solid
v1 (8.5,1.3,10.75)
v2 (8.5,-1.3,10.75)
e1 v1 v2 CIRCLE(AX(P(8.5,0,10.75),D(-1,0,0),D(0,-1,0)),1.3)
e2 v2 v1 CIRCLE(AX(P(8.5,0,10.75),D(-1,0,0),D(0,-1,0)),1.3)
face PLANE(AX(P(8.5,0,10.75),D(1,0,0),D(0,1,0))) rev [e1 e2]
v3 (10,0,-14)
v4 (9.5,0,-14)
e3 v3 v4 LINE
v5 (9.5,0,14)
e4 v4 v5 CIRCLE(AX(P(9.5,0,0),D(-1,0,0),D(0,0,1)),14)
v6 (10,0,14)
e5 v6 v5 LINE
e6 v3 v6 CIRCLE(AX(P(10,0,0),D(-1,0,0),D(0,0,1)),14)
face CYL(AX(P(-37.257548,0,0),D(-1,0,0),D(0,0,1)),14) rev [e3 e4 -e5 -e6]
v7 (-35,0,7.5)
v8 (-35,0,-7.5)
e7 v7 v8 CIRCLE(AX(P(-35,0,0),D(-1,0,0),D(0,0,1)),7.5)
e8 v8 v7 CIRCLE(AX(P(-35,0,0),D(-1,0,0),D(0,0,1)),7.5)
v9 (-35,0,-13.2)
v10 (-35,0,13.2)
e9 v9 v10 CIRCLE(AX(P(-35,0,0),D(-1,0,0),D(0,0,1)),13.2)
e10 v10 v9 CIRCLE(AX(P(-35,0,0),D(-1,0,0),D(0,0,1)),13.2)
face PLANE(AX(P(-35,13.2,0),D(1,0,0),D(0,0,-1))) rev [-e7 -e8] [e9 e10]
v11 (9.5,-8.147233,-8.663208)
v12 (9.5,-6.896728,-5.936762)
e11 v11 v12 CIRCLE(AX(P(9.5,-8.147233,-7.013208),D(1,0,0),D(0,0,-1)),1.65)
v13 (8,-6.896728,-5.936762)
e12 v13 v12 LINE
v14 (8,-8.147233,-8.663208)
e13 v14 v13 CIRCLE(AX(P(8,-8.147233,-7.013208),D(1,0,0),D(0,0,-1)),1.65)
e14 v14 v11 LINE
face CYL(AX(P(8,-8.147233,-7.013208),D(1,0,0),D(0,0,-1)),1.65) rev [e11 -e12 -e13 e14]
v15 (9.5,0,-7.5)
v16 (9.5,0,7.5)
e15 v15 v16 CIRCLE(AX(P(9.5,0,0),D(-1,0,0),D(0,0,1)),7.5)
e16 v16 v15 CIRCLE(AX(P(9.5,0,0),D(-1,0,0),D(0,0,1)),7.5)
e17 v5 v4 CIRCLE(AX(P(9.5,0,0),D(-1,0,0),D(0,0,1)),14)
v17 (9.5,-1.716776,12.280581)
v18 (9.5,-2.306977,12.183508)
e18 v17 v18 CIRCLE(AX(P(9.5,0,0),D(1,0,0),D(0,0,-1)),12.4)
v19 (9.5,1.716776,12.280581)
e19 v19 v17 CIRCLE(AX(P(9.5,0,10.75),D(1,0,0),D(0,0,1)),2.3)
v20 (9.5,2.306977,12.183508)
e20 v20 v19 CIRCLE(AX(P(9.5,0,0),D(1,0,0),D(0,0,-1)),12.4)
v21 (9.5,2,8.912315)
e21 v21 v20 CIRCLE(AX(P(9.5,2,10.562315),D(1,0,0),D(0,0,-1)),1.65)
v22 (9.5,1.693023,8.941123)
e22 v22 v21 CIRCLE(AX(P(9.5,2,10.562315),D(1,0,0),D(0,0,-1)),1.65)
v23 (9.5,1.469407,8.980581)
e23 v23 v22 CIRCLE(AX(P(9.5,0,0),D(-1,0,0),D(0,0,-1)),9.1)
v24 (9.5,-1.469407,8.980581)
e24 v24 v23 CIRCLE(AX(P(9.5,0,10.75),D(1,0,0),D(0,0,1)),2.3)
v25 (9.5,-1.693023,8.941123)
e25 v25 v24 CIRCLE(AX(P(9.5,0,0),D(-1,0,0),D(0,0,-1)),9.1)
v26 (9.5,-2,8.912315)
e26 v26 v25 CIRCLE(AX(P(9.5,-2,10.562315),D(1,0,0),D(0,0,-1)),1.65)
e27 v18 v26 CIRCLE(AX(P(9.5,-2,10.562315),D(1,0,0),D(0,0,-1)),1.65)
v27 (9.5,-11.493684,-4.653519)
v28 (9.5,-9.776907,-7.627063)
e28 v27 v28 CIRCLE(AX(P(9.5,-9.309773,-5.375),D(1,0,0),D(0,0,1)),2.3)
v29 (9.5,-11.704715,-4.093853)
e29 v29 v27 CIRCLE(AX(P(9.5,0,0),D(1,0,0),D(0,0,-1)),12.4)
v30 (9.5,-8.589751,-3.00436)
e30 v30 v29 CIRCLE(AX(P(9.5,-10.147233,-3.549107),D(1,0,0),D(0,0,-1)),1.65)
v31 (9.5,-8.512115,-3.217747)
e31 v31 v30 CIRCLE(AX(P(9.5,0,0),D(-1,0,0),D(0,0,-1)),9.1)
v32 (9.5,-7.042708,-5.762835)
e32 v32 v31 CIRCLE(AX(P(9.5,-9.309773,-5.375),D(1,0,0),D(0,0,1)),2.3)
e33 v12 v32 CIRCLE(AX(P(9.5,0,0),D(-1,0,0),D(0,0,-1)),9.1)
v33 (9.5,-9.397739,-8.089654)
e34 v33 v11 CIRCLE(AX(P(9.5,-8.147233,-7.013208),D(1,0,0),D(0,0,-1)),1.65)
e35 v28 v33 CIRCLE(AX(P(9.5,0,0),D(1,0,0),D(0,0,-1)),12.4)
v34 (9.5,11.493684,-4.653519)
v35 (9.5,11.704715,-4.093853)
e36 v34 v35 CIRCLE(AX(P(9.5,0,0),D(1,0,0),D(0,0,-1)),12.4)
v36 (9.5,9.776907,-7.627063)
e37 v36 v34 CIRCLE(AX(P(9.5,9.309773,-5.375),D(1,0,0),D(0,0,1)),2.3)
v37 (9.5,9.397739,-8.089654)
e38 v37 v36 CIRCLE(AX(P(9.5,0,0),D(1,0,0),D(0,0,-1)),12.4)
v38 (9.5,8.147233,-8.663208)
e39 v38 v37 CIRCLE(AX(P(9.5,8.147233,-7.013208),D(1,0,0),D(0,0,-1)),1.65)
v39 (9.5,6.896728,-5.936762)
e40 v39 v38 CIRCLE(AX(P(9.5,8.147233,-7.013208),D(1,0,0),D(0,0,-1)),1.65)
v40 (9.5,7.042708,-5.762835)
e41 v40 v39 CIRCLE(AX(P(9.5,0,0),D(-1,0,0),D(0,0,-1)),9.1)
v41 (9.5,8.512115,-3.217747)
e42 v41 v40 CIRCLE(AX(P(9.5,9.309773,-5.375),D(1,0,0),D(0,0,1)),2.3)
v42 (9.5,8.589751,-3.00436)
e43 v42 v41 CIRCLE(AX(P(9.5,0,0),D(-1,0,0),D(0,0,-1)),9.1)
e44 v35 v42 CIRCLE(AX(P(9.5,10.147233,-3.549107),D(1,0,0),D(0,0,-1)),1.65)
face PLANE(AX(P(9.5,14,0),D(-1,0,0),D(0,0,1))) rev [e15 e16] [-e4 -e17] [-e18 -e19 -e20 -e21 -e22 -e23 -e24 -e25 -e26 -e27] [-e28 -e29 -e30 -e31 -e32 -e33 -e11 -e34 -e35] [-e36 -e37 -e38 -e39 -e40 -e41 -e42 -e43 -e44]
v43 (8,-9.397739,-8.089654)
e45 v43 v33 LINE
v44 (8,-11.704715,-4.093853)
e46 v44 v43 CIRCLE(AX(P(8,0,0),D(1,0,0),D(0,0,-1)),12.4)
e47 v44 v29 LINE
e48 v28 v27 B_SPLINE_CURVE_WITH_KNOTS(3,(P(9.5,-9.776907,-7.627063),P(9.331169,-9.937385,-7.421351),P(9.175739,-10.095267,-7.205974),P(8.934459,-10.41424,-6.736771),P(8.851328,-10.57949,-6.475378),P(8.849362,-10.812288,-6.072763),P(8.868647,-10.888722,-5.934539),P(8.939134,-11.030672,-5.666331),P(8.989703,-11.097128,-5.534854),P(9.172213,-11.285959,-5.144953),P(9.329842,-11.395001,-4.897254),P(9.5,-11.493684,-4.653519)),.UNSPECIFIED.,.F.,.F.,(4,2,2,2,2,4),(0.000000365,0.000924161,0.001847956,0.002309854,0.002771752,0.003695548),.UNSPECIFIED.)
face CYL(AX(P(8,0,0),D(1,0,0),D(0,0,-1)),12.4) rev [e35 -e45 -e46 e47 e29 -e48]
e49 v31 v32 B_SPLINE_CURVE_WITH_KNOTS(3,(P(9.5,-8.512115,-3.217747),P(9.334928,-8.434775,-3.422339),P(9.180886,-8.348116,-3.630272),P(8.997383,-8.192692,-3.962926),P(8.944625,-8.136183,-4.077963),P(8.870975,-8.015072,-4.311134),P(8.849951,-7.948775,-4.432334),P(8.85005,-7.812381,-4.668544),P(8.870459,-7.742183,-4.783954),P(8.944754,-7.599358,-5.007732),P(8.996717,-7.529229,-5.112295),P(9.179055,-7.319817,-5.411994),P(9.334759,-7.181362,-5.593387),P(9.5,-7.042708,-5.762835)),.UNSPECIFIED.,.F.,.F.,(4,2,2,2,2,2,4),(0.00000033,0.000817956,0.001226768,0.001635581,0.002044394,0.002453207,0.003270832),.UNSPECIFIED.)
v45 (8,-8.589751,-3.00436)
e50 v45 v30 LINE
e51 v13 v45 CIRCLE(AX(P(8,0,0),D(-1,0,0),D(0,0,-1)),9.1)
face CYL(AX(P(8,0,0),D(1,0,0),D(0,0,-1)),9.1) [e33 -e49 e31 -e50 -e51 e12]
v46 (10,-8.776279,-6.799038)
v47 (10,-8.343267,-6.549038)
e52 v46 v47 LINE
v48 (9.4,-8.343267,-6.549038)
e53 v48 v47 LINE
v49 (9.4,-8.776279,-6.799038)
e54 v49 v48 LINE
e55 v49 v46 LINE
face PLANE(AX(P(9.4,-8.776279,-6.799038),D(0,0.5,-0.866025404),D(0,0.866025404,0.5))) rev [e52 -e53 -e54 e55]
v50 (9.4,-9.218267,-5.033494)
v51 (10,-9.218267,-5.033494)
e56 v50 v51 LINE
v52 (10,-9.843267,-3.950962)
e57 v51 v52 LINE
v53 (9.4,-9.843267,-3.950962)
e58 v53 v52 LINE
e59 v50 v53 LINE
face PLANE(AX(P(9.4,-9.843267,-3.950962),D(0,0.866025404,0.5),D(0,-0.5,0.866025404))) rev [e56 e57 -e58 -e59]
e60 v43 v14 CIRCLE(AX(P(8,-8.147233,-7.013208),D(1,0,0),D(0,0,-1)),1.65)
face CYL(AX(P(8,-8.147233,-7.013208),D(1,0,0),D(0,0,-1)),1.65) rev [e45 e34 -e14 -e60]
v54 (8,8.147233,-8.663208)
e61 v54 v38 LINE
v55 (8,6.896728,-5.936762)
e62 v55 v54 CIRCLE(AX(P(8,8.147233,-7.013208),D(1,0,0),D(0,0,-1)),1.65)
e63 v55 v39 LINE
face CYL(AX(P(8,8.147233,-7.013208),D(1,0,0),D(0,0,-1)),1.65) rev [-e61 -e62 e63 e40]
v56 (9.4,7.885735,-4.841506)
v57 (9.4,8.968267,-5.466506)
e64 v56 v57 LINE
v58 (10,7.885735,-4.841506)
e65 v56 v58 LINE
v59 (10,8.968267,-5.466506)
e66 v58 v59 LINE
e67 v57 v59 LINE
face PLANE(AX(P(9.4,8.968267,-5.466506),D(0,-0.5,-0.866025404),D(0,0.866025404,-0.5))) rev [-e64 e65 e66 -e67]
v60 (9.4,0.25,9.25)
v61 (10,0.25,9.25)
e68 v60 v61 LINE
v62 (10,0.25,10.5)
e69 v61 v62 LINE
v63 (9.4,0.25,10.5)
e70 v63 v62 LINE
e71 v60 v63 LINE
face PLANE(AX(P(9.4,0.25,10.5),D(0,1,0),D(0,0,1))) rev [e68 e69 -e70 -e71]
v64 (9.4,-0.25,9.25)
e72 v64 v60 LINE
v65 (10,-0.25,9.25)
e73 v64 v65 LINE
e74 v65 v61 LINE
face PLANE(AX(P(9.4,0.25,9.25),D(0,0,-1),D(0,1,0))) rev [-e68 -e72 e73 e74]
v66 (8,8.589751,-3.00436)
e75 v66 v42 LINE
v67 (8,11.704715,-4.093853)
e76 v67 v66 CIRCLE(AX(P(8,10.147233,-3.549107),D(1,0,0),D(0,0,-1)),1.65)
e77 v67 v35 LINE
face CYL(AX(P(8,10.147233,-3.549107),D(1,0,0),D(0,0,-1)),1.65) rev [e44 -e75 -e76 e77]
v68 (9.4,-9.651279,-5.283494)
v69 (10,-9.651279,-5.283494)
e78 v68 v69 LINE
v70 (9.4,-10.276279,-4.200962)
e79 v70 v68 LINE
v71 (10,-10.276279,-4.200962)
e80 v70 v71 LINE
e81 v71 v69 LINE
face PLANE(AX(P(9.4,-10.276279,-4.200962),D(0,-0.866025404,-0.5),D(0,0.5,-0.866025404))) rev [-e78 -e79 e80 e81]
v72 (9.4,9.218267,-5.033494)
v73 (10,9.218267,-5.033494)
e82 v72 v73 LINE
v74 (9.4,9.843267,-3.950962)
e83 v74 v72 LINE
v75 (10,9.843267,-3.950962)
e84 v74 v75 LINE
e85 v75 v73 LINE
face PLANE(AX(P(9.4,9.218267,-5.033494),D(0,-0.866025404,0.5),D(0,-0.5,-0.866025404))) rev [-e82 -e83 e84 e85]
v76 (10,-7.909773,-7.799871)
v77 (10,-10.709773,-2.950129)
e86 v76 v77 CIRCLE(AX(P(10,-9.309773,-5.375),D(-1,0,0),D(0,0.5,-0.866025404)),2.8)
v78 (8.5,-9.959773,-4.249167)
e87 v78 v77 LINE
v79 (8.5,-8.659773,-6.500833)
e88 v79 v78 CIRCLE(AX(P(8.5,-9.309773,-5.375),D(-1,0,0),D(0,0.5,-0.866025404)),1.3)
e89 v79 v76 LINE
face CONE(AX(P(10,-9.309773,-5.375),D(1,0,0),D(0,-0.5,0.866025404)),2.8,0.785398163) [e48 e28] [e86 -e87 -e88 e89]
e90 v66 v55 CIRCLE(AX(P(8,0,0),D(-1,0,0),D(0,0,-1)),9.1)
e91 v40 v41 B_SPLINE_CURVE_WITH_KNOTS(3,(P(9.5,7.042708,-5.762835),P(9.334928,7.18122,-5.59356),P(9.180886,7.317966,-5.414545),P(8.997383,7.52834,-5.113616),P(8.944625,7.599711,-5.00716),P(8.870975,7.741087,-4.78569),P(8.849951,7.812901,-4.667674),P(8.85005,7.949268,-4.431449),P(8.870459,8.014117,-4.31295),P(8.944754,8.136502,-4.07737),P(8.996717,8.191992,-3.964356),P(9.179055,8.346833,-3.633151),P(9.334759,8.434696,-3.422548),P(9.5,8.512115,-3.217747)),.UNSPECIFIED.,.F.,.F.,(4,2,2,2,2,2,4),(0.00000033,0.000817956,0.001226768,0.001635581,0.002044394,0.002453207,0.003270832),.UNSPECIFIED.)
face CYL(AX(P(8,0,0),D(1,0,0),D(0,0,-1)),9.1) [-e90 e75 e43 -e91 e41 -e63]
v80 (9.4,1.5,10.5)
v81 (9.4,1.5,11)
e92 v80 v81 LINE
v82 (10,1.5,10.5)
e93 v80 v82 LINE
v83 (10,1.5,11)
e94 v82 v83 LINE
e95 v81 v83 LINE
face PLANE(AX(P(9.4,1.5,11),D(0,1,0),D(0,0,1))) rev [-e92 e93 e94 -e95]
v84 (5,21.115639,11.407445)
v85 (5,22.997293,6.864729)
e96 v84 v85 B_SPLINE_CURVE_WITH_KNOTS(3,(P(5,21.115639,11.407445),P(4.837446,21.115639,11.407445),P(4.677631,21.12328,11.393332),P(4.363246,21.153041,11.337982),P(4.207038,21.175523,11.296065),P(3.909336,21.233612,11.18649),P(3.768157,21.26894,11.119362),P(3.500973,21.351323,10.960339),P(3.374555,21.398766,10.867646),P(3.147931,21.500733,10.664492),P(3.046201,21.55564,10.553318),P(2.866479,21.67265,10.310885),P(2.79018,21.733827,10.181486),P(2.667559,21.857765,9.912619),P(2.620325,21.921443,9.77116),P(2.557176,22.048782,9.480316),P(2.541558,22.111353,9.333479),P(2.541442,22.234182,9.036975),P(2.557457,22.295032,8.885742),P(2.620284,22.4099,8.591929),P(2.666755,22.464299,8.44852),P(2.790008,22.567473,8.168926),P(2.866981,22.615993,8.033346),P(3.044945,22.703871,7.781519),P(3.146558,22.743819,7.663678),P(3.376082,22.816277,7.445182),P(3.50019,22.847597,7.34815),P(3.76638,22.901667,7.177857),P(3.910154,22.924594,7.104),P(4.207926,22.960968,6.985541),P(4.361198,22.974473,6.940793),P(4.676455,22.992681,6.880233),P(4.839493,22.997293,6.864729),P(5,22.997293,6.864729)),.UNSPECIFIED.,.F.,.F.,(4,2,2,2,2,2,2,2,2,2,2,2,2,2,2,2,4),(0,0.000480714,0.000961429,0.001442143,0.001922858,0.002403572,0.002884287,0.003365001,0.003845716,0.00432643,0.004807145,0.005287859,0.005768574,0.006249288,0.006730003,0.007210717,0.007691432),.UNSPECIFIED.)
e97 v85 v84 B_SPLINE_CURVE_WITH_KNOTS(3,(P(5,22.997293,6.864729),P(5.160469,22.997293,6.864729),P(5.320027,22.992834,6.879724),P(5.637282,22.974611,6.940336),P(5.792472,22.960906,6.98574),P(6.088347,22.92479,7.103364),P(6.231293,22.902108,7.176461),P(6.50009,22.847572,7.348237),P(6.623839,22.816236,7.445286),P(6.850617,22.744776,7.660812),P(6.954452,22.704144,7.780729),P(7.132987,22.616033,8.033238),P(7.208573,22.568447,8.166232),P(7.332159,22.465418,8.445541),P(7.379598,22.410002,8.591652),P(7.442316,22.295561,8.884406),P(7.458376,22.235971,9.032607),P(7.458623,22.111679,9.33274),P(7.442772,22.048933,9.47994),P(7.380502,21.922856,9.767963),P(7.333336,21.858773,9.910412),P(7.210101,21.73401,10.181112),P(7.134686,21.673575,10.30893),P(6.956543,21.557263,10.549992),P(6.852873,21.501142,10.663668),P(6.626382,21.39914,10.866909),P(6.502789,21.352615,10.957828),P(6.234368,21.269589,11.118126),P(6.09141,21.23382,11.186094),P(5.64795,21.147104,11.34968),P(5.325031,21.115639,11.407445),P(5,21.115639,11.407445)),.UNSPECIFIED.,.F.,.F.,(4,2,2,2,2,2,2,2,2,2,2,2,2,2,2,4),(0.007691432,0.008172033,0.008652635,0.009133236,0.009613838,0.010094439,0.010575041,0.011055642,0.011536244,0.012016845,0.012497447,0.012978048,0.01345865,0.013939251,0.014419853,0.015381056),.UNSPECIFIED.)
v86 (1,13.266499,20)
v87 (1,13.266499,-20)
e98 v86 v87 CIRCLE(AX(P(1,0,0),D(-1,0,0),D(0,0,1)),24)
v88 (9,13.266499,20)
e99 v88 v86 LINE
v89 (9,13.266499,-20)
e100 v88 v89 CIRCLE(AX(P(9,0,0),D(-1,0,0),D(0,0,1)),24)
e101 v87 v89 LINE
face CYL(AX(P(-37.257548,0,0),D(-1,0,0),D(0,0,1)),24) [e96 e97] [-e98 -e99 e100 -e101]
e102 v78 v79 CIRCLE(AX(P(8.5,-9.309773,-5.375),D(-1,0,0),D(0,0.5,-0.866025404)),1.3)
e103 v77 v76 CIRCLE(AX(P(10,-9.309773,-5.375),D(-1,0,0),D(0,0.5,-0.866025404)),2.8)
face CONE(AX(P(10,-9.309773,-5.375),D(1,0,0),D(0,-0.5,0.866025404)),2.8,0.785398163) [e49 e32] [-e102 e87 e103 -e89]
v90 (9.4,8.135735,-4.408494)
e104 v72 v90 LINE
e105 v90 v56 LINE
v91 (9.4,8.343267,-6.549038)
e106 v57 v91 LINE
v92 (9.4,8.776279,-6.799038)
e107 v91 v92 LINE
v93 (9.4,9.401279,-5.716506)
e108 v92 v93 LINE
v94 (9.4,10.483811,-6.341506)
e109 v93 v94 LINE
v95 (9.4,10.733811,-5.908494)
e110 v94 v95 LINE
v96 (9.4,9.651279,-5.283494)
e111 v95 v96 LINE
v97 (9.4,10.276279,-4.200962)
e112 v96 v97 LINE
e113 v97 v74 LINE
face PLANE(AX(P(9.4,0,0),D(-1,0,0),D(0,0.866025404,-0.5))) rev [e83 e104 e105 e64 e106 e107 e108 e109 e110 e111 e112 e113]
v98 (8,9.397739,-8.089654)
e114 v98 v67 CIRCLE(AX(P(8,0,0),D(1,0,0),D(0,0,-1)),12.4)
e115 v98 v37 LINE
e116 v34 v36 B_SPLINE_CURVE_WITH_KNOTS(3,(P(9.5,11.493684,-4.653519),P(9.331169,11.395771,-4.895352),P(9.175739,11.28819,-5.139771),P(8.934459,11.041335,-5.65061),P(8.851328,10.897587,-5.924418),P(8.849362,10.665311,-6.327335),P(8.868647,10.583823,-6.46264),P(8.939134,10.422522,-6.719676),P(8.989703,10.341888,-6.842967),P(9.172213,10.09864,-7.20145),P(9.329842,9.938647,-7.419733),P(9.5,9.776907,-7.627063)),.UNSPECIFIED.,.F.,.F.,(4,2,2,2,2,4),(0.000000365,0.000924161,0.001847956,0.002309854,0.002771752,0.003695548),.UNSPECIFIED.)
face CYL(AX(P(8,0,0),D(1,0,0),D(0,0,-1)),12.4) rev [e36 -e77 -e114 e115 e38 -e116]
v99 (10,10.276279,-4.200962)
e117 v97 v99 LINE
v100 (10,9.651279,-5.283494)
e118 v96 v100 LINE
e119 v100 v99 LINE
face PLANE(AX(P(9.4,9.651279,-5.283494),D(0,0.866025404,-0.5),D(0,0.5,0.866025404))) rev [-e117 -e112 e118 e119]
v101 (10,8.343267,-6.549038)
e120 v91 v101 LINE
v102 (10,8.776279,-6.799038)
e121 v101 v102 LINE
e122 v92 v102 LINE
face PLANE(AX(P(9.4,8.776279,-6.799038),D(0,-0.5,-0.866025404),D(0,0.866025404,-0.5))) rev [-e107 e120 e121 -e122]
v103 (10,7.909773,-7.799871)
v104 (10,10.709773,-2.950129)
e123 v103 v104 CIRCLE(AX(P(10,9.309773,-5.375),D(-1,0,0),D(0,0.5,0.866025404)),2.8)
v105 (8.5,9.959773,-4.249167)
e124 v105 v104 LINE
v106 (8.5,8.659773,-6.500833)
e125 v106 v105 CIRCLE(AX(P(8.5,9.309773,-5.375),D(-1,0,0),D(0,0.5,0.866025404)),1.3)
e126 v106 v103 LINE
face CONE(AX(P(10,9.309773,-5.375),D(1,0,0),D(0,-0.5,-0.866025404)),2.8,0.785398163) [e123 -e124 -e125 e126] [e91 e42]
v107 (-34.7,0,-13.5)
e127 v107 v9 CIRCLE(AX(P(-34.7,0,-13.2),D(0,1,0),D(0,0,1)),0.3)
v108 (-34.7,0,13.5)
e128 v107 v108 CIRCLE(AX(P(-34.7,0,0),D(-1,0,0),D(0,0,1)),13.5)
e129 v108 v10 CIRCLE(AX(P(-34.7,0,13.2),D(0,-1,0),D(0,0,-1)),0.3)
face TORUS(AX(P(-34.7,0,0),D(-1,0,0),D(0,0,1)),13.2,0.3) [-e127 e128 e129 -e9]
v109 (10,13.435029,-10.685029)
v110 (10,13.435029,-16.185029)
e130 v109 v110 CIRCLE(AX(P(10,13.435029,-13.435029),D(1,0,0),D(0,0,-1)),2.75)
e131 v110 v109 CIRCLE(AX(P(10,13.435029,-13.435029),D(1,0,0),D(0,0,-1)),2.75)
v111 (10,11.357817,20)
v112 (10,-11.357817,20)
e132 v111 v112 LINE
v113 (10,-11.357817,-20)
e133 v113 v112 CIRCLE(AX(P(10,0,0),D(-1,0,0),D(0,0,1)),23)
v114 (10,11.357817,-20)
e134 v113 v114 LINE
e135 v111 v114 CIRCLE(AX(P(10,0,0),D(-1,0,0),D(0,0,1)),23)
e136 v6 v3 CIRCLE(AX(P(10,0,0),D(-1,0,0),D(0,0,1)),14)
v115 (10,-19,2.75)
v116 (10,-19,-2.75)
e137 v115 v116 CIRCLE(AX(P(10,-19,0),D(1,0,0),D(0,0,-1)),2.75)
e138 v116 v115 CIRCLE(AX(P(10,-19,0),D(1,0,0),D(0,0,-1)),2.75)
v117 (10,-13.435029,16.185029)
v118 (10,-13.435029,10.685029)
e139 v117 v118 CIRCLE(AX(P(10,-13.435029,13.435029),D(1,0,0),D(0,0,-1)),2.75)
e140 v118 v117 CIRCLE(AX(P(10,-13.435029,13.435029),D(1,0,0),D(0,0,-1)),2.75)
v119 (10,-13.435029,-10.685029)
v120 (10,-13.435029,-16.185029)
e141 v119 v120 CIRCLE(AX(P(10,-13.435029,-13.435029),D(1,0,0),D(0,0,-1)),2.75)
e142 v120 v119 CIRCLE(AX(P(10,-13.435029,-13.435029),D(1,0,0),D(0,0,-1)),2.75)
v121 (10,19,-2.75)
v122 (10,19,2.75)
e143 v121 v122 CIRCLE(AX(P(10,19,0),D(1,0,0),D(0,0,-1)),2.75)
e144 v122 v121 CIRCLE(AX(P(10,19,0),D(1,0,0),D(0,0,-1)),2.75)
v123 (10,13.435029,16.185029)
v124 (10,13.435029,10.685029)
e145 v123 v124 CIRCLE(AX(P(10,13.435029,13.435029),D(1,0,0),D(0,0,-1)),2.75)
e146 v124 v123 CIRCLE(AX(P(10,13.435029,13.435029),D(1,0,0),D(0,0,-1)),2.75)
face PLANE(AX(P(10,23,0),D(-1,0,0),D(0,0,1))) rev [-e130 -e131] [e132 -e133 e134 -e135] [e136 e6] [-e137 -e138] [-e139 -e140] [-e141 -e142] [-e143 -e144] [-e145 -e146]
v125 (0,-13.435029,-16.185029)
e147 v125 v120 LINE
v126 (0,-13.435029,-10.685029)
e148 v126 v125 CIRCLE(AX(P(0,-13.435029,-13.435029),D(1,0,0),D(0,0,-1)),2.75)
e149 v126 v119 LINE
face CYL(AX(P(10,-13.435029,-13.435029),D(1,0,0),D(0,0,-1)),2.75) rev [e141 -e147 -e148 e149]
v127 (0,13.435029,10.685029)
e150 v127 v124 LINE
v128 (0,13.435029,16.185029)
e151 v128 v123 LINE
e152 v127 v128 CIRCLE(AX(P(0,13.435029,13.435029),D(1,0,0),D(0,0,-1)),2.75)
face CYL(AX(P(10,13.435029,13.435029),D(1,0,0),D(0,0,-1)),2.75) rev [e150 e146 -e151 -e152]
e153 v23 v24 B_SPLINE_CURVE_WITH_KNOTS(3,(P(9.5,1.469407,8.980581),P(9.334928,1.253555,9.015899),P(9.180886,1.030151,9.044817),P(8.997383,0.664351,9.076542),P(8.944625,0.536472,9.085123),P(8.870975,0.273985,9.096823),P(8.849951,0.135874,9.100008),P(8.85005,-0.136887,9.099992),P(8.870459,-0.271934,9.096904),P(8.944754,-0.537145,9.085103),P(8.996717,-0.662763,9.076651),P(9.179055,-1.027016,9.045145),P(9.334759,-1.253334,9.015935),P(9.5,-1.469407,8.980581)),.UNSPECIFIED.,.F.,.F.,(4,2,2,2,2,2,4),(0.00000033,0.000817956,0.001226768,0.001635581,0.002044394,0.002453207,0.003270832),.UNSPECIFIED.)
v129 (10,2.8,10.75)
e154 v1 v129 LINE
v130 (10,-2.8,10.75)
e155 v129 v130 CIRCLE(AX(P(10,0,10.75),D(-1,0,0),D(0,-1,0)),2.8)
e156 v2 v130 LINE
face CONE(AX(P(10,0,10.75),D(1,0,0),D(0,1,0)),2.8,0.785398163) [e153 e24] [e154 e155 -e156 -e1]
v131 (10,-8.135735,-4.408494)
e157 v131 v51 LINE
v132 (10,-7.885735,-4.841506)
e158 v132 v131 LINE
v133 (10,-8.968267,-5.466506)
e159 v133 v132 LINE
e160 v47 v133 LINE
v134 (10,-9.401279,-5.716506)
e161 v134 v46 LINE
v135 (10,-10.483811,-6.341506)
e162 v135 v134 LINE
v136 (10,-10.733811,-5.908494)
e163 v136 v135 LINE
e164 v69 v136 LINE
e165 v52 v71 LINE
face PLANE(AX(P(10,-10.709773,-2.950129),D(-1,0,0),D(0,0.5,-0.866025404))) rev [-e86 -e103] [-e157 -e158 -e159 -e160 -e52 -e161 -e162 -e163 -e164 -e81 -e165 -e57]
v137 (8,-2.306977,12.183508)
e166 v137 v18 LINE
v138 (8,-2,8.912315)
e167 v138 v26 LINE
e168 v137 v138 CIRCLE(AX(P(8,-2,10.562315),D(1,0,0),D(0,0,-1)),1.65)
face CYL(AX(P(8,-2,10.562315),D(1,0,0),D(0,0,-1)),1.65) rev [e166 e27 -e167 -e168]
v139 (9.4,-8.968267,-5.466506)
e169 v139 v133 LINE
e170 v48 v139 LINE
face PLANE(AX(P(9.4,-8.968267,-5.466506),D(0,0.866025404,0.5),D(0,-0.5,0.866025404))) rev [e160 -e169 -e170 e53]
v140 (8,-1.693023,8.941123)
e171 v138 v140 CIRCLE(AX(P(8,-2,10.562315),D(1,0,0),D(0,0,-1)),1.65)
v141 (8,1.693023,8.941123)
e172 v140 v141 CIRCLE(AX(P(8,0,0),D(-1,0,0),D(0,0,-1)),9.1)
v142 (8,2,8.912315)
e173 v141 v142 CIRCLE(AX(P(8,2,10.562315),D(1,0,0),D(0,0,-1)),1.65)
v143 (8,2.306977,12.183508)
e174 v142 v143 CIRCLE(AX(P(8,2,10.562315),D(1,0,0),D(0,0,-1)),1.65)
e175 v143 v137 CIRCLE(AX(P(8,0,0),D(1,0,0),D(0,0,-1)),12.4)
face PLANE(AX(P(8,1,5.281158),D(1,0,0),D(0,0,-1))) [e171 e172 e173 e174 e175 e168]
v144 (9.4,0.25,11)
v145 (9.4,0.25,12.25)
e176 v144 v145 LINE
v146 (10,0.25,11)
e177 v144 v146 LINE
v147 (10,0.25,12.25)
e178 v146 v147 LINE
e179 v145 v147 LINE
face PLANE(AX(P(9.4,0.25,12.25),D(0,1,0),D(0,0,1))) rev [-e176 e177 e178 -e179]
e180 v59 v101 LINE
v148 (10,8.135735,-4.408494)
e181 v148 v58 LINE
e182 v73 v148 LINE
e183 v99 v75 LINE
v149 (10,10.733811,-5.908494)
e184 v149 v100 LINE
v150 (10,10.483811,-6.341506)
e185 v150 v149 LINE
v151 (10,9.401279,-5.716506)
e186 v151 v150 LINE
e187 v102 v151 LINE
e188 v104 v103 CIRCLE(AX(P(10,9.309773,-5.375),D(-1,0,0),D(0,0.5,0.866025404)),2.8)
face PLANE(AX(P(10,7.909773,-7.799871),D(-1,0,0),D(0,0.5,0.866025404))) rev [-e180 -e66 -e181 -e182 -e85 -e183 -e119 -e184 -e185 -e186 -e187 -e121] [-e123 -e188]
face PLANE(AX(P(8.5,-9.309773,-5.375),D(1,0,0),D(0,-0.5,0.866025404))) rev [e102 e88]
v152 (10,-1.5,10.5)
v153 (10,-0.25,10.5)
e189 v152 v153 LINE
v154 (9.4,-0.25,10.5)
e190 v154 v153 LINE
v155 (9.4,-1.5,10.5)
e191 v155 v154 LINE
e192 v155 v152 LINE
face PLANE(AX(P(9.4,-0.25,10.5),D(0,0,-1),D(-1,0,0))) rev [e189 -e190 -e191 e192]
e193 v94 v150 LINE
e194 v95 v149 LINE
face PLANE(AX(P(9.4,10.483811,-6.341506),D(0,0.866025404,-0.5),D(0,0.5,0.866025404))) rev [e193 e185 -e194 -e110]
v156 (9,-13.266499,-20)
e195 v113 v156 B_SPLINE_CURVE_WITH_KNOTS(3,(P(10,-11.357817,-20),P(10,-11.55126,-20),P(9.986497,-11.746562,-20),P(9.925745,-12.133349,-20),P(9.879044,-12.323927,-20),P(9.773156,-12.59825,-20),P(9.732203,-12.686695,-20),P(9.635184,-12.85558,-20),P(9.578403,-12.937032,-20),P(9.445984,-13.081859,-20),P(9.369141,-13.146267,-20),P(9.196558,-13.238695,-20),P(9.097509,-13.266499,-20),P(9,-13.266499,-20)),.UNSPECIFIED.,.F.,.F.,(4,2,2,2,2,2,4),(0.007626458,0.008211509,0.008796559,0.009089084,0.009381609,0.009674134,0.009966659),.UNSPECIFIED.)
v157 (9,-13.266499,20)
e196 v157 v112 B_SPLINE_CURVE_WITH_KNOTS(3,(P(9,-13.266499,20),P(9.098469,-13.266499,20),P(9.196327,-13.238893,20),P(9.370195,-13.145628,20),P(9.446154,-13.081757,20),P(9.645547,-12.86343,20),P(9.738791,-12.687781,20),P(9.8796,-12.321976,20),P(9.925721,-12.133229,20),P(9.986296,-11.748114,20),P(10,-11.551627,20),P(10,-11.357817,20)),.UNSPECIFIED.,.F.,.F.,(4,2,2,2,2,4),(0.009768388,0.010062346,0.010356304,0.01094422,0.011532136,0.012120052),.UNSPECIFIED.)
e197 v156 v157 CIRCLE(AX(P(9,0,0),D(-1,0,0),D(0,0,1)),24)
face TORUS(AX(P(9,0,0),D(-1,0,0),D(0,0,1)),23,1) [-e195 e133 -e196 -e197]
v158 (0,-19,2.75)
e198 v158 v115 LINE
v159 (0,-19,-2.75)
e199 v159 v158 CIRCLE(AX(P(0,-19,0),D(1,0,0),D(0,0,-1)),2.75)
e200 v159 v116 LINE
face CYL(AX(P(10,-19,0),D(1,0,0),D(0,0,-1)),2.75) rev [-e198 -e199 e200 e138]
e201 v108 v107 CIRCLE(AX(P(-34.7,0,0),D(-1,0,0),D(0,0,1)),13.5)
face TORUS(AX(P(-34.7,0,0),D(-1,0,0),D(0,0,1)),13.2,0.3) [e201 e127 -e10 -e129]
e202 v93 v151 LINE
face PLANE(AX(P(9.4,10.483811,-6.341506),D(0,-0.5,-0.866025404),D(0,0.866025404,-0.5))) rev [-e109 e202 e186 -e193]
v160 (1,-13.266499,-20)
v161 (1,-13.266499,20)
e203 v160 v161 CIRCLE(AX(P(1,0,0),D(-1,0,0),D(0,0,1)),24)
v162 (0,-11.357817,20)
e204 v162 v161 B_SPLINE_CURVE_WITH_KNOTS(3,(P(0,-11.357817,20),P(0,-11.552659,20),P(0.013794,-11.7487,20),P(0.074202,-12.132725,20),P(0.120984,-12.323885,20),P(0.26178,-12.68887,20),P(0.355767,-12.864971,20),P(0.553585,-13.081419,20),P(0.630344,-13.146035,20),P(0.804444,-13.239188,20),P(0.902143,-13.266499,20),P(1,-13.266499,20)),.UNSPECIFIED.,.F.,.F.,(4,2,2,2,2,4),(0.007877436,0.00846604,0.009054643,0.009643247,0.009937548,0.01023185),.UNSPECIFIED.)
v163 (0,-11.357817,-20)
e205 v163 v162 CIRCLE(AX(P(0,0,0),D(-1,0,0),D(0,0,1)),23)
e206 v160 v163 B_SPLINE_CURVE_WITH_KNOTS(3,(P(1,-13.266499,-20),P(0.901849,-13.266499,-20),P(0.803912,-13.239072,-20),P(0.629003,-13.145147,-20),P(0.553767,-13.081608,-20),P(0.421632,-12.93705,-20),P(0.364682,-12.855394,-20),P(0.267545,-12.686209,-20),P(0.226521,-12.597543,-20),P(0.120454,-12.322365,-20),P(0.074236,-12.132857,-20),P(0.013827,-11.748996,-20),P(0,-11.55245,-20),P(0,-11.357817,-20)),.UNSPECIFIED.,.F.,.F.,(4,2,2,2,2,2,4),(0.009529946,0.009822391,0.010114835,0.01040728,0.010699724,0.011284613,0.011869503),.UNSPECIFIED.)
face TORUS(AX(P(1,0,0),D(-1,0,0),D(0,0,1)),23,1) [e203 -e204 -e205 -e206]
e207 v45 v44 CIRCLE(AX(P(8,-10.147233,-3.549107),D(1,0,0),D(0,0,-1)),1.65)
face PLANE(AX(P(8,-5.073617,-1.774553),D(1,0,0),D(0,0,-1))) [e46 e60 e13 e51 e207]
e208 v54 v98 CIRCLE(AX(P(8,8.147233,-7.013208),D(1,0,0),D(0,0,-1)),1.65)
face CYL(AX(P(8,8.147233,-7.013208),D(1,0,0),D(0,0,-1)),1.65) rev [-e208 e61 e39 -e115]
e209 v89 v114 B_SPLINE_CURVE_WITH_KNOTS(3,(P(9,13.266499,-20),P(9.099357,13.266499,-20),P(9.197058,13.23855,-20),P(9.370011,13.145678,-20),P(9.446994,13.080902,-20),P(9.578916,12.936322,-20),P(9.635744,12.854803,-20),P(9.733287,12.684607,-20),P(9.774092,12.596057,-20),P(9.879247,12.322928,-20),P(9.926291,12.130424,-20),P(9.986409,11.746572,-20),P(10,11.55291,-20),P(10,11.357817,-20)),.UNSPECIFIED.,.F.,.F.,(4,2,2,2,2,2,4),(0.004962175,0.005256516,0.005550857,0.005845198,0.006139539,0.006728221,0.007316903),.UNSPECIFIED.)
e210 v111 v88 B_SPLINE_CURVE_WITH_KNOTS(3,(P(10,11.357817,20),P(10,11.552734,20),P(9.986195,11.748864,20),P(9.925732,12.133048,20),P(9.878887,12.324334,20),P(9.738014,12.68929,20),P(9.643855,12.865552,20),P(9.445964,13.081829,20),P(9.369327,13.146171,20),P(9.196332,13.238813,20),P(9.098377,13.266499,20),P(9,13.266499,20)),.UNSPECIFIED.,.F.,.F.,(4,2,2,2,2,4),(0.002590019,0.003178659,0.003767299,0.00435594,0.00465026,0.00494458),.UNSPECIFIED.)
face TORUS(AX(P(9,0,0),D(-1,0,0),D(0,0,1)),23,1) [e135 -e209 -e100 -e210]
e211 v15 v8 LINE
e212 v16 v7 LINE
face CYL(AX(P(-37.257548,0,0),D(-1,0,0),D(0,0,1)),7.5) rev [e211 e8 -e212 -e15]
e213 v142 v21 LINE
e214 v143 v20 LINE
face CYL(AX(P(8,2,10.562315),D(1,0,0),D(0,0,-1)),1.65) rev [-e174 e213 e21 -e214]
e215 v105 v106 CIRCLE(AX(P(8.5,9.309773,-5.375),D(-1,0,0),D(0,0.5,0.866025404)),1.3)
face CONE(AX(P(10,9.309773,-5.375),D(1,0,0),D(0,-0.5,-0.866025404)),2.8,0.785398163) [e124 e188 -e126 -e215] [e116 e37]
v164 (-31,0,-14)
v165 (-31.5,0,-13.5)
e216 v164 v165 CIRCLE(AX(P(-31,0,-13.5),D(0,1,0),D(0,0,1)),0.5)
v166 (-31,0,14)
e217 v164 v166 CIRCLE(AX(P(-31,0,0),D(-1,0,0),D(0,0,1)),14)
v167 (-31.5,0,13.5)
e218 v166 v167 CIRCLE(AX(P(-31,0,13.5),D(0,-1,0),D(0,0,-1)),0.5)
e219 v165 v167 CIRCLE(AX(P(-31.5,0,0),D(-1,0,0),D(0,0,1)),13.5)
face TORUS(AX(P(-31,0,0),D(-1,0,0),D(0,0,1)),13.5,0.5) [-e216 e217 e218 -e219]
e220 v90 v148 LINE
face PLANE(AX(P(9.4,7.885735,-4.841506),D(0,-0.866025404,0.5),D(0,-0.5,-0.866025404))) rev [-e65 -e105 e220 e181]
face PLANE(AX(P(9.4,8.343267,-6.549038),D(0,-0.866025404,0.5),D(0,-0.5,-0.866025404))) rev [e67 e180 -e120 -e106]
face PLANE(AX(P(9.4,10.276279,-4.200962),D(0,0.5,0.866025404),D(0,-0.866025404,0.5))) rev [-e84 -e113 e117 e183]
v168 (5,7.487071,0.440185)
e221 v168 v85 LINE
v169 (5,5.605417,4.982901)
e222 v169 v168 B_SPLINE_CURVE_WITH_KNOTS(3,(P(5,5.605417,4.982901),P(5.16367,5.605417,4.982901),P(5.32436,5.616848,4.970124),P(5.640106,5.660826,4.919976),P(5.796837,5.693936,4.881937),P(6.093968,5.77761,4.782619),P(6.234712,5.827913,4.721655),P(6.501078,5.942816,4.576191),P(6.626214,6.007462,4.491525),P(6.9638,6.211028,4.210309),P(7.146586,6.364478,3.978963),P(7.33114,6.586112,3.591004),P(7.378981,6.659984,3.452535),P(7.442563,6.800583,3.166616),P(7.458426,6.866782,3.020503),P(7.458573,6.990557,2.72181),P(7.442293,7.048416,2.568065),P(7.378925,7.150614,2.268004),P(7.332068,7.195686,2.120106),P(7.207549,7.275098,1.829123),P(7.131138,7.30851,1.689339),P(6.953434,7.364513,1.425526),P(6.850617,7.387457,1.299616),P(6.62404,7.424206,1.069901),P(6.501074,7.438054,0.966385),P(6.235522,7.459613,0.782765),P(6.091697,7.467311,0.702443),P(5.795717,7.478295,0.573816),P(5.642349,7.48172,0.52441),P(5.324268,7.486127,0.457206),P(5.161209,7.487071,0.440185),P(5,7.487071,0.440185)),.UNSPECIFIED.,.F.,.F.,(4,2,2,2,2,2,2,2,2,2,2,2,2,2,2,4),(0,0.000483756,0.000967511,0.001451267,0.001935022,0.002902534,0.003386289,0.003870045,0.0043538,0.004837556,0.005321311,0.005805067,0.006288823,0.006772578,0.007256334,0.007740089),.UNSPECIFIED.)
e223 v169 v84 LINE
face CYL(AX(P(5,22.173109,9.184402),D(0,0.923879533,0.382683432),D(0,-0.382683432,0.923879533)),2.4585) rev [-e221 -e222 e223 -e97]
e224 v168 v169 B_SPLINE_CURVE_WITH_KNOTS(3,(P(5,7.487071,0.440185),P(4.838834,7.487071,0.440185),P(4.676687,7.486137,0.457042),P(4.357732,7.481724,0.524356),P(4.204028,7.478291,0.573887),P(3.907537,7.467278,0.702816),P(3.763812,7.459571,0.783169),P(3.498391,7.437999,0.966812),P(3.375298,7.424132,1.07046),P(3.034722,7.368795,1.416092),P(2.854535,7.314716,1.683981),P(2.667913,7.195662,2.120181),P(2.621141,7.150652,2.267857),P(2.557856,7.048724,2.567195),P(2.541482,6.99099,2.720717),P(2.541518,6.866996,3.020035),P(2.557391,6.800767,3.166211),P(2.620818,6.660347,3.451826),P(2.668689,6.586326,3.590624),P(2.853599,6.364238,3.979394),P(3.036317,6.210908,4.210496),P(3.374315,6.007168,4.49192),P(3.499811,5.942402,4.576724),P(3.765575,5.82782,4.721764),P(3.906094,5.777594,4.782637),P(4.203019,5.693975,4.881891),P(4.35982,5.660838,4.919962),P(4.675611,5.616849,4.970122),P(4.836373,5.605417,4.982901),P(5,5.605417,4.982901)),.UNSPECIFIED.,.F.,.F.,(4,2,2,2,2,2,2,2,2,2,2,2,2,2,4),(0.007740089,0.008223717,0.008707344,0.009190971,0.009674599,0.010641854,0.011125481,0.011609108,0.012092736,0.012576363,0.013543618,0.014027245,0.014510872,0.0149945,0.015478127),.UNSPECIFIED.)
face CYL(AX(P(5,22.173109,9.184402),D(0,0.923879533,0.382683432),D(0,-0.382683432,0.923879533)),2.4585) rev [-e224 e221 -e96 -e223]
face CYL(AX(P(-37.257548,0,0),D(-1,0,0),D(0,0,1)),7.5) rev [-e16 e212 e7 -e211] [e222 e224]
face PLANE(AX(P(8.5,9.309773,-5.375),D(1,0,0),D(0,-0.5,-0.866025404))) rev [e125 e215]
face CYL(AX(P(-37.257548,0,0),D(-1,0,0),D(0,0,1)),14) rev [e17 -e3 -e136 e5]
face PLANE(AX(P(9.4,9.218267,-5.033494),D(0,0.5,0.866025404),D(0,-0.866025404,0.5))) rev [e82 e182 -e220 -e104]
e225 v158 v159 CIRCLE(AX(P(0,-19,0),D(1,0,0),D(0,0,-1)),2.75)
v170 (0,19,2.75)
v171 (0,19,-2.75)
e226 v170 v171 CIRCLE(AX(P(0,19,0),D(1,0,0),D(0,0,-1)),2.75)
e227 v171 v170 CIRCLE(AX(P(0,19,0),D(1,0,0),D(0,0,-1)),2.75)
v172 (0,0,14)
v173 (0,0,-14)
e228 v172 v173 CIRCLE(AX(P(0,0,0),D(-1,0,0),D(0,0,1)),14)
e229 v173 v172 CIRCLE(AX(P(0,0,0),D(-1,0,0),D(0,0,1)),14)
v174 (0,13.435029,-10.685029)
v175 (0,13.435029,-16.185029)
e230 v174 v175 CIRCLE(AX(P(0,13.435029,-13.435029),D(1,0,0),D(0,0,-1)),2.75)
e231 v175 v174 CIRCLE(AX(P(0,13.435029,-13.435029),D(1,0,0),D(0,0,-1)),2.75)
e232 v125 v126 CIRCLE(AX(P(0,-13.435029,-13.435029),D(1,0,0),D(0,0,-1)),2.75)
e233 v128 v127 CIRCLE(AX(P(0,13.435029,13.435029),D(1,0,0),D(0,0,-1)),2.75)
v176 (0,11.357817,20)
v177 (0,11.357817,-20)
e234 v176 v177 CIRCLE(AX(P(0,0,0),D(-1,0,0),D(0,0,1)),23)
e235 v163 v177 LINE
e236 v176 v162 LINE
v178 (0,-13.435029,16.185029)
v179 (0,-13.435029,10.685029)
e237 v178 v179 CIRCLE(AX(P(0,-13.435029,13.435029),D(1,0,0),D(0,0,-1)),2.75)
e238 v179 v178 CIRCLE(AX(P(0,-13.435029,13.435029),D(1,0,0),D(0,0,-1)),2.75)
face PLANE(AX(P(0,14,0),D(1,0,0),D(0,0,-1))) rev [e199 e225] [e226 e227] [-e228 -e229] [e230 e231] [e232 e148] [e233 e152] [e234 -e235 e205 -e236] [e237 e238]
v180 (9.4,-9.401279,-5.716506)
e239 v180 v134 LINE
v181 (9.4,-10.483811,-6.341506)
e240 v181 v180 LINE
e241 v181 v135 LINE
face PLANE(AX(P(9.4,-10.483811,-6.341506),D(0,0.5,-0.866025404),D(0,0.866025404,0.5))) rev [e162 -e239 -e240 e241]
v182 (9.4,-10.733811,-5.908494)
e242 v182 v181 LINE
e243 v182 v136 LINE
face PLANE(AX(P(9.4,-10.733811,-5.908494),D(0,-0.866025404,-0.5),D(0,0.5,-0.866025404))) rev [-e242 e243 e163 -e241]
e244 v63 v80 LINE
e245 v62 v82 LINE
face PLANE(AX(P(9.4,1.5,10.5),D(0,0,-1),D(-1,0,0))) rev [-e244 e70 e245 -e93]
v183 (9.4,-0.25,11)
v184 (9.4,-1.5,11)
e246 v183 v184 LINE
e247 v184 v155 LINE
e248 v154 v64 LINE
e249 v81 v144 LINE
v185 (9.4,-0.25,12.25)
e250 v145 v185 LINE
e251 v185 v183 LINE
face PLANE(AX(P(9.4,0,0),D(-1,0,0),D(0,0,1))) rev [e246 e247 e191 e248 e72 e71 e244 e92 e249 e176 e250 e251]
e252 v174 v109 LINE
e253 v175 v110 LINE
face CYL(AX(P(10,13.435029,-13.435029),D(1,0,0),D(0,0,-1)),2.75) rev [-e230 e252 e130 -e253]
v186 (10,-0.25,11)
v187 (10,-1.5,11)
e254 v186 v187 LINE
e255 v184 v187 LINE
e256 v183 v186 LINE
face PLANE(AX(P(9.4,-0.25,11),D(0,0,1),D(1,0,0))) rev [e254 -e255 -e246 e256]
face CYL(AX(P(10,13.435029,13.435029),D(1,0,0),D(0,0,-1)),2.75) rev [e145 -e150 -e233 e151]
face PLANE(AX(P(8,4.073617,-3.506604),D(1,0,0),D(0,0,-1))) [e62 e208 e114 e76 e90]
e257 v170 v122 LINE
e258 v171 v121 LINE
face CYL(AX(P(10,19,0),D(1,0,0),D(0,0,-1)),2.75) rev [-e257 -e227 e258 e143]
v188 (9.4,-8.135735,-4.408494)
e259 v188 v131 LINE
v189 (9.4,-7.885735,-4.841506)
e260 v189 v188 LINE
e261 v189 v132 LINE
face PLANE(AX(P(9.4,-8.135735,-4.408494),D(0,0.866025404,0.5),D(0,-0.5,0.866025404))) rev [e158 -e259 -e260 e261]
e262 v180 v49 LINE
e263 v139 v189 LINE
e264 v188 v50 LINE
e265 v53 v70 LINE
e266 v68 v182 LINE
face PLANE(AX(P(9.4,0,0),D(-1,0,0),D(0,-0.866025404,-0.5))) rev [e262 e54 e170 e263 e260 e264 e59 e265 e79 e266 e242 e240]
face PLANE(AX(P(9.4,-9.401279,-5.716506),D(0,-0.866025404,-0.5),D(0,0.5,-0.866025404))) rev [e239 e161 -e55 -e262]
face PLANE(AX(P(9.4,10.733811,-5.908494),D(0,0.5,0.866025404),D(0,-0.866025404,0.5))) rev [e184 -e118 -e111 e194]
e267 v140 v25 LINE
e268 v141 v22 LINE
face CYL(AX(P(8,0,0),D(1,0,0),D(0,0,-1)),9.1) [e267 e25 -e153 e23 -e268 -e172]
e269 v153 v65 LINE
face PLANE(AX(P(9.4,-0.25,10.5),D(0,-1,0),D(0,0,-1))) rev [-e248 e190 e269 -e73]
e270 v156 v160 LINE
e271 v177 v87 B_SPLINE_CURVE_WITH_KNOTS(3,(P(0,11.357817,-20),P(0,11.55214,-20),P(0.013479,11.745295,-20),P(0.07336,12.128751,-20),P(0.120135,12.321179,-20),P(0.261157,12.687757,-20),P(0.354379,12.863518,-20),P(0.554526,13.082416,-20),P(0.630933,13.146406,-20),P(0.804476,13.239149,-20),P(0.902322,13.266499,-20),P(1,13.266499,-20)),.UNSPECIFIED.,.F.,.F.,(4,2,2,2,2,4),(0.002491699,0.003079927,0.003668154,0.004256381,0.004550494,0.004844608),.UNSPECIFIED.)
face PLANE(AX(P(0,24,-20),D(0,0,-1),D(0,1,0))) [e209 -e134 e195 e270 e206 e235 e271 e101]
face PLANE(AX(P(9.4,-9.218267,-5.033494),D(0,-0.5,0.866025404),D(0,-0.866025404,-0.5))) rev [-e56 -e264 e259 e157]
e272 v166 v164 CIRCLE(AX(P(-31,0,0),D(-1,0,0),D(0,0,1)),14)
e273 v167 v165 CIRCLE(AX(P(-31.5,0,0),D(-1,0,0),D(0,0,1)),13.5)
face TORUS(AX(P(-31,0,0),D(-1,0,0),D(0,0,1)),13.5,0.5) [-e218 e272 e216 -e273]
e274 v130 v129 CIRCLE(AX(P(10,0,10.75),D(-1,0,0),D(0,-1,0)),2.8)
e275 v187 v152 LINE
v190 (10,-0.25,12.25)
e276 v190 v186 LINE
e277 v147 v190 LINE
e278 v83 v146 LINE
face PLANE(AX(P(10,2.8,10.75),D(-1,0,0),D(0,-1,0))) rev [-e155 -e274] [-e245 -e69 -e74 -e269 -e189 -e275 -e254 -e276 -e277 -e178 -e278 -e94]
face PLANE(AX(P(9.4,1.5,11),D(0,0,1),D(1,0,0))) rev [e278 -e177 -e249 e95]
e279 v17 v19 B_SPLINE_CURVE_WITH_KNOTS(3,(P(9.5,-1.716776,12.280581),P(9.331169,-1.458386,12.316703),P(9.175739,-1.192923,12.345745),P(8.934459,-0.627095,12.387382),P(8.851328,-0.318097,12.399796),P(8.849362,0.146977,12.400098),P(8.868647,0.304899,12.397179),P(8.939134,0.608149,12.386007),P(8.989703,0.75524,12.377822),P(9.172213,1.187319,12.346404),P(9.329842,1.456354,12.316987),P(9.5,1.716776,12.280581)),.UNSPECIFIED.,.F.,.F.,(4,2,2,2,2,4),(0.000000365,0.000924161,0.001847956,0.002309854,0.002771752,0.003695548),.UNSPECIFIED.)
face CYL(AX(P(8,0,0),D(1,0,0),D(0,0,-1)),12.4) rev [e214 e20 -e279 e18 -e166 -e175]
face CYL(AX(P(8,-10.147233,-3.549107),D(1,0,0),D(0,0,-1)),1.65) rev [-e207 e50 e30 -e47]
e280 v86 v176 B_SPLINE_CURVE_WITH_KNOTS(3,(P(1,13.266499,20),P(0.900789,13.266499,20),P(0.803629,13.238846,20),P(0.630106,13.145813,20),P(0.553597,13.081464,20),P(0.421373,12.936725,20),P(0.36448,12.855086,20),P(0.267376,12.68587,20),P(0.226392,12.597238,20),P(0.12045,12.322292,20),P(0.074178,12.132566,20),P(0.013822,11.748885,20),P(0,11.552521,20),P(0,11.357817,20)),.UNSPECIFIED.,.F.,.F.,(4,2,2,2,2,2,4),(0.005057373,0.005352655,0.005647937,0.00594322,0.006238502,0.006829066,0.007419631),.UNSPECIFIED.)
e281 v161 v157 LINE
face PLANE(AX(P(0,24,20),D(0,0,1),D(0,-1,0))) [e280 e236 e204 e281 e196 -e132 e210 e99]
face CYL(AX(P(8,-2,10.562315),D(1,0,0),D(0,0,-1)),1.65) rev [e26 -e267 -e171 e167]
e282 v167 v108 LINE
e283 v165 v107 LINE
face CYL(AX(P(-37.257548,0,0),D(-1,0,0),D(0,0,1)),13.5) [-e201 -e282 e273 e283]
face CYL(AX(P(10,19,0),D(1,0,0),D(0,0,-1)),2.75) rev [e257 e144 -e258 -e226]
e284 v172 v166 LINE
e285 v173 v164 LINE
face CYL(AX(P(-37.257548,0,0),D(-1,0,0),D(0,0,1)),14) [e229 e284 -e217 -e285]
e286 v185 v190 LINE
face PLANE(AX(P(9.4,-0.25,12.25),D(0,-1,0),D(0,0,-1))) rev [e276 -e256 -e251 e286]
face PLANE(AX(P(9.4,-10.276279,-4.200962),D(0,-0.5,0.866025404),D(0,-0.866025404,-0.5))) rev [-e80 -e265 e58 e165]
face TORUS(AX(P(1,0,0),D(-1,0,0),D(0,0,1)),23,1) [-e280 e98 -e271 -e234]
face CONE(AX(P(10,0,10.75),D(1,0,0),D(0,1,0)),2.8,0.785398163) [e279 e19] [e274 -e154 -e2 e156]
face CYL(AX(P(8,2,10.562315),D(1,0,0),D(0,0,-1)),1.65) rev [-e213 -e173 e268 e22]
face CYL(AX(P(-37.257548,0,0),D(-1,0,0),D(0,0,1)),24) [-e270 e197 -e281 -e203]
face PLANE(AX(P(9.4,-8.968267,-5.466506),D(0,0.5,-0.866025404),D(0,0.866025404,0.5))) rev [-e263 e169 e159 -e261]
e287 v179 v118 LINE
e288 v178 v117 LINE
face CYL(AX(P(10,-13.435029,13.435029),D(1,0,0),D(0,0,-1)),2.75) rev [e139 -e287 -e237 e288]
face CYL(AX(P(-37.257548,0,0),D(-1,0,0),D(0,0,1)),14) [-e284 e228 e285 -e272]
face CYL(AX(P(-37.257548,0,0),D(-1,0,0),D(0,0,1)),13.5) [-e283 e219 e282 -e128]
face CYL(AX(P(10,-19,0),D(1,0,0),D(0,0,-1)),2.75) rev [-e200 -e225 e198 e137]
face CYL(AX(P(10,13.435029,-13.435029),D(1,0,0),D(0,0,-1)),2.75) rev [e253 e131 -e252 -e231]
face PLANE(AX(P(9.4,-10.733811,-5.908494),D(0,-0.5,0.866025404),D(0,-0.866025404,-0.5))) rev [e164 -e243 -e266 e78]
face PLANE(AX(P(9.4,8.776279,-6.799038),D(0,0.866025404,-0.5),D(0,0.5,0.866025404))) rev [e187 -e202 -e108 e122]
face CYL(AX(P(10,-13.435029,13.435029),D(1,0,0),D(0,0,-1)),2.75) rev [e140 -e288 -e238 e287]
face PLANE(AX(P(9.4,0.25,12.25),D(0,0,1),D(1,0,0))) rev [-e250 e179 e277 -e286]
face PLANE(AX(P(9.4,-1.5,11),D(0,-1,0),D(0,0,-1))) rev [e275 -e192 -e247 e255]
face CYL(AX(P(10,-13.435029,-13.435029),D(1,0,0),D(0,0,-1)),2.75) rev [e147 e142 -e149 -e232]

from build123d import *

# Parameters (mm, degrees)
SKETCH2_OUTSIDE_W   = 66.288
SKETCH2_OUTSIDE_H   = 66.288
SKETCH2_OUTSIDE_W_2 = 40
SKETCH2_OUTSIDE_H_2 = 48
CUT_EXTRUDE1_DEPTH  = 10
DIAMETERHOLE1_D     = 5.5
TAP1_REACH          = 66.874
TAP1_BORE_R         = 2.4585
CUT_EXTRUDE2_DEPTH  = 1.5
CUT_EXTRUDE3_DEPTH  = 0.6
CIRPATTERN1_COUNT   = 3


with BuildPart() as part:
    # Sketch1 → Revolve1 (revolve)
    with BuildSketch(Plane.XY, mode=Mode.PRIVATE) as revolve1_sk:
        with BuildLine():
            Line((10, 14), (9.5, 14))
            Line((9.5, 14), (9.5, 7.5))
            Line((9.5, 7.5), (-35, 7.5))
            Line((-35, 7.5), (-35, 13.2))
            ThreePointArc((-35, 13.2), (-34.912132034, 13.412132034), (-34.7, 13.5))
            Line((-34.7, 13.5), (-31.5, 13.5))
            ThreePointArc((-31.5, 13.5), (-31.353553391, 13.853553391), (-31, 14))
            Line((-31, 14), (0, 14))
            Line((0, 14), (0, 23))
            ThreePointArc((0, 23), (0.292893219, 23.707106781), (1, 24))
            Line((1, 24), (9, 24))
            ThreePointArc((9, 24), (9.707106781, 23.707106781), (10, 23))
            Line((10, 23), (10, 14))
        make_face()
    revolve(revolve1_sk.sketch.rotate(Axis((-37.257548112, 0, 0), (1, 0, 0)), 90), axis=Axis((-37.257548112, 0, 0), (1, 0, 0)))

    # Sketch2 outside → Cut-Extrude1 (cut)
    with BuildSketch(Plane(origin=(10, 0, 0), x_dir=(0, 0, -1), z_dir=(1, 0, 0))):
        Rectangle(SKETCH2_OUTSIDE_W, SKETCH2_OUTSIDE_H)
        Rectangle(SKETCH2_OUTSIDE_W_2, SKETCH2_OUTSIDE_H_2, mode=Mode.SUBTRACT)
    extrude(amount=-CUT_EXTRUDE1_DEPTH, mode=Mode.SUBTRACT)

    # DiameterHole1 (through all)
    with Locations(Plane(origin=(10, 0, 0), x_dir=(0, 0, -1), z_dir=(1, 0, 0))):
        with Locations((13.435028843, 13.435028843), (0, 19), (-13.435028843, 13.435028843), (-13.435028843, -13.435028843), (0, -19), (13.435028843, -13.435028843)):
            Hole(DIAMETERHOLE1_D / 2)

    # Tap1 bore → Tap1 (cut, up to next)
    with BuildSketch(Plane(origin=(0, 22.17310878, 9.184402377), x_dir=(1, 0, 0), z_dir=(0, 0.9238795325112865, 0.3826834323650906)), mode=Mode.PRIVATE) as tap1_sk1:
        with Locations((5, 0)):
            Circle(TAP1_BORE_R)
    tap1_tool1 = extrude(tap1_sk1.sketch, amount=-TAP1_REACH, mode=Mode.PRIVATE) & part.part
    add(tap1_tool1.solids().sort_by_distance((5, 22.173109, 9.184402))[0], mode=Mode.SUBTRACT)

    # Sketch7 → Cut-Extrude2 (cut)
    with BuildSketch(Plane(origin=(9.5, 0, 0), x_dir=(0, 0, -1), z_dir=(1, 0, 0))):
        with BuildLine():
            ThreePointArc((-12.183507635, 2.306976744), (-12.4, 0), (-12.183507635, -2.306976744))
            ThreePointArc((-12.183507635, -2.306976744), (-10.255338343, -3.621192548), (-8.941122539, -1.693023256))
            ThreePointArc((-8.941122539, -1.693023256), (-9.1, 0), (-8.941122539, 1.693023256))
            ThreePointArc((-8.941122539, 1.693023256), (-10.255338343, 3.621192548), (-12.183507635, 2.306976744))
        make_face()
        with BuildLine():
            ThreePointArc((8.089654284, 9.397738747), (6.2, 10.738715007), (4.093853351, 11.704715492))
            ThreePointArc((4.093853351, 11.704715492), (1.991624433, 10.691979804), (3.004360121, 8.589750885))
            ThreePointArc((3.004360121, 8.589750885), (4.55, 7.880831174), (5.936762418, 6.896727629))
            ThreePointArc((5.936762418, 6.896727629), (8.26371391, 7.070787255), (8.089654284, 9.397738747))
        make_face()
        with BuildLine():
            ThreePointArc((4.093853351, -11.704715492), (6.2, -10.738715007), (8.089654284, -9.397738747))
            ThreePointArc((8.089654284, -9.397738747), (8.26371391, -7.070787255), (5.936762418, -6.896727629))
            ThreePointArc((5.936762418, -6.896727629), (4.55, -7.880831174), (3.004360121, -8.589750885))
            ThreePointArc((3.004360121, -8.589750885), (1.991624433, -10.691979804), (4.093853351, -11.704715492))
        make_face()
    extrude(amount=-CUT_EXTRUDE2_DEPTH, mode=Mode.SUBTRACT)

    # Sketch8 → Revolve2 (revolve)
    with BuildSketch(Plane.XY.offset(10.75), mode=Mode.PRIVATE) as revolve2_sk:
        Polygon((8.5, 1.3), (10, 2.8), (10, 0), (8.5, 0), align=None)
    revolve2 = revolve(revolve2_sk.sketch.rotate(Axis((0, 0, 10.75), (1, 0, 0)), 180), axis=Axis((0, 0, 10.75), (1, 0, 0)))

    # Sketch9 → Cut-Extrude3 (cut)
    with BuildSketch(Plane(origin=(10, 0, 0), x_dir=(0, 0, -1), z_dir=(1, 0, 0))):
        Polygon((-12.25, 0.25), (-11, 0.25), (-11, 1.5), (-10.5, 1.5), (-10.5, 0.25), (-9.25, 0.25), (-9.25, -0.25), (-10.5, -0.25), (-10.5, -1.5), (-11, -1.5), (-11, -0.25), (-12.25, -0.25), align=None)
    cut_extrude3 = extrude(amount=-CUT_EXTRUDE3_DEPTH, mode=Mode.SUBTRACT)

    # CirPattern1: Revolve2, Cut-Extrude3 ×3 about axis
    cirpattern1_axis = Axis((0, 0, 0), (1, 0, 0))
    add([revolve2.rotate(cirpattern1_axis, i * 360 / CIRPATTERN1_COUNT) for i in range(1, CIRPATTERN1_COUNT)])
    add([cut_extrude3.rotate(cirpattern1_axis, i * 360 / CIRPATTERN1_COUNT) for i in range(1, CIRPATTERN1_COUNT)], mode=Mode.SUBTRACT)


solid = part.part
